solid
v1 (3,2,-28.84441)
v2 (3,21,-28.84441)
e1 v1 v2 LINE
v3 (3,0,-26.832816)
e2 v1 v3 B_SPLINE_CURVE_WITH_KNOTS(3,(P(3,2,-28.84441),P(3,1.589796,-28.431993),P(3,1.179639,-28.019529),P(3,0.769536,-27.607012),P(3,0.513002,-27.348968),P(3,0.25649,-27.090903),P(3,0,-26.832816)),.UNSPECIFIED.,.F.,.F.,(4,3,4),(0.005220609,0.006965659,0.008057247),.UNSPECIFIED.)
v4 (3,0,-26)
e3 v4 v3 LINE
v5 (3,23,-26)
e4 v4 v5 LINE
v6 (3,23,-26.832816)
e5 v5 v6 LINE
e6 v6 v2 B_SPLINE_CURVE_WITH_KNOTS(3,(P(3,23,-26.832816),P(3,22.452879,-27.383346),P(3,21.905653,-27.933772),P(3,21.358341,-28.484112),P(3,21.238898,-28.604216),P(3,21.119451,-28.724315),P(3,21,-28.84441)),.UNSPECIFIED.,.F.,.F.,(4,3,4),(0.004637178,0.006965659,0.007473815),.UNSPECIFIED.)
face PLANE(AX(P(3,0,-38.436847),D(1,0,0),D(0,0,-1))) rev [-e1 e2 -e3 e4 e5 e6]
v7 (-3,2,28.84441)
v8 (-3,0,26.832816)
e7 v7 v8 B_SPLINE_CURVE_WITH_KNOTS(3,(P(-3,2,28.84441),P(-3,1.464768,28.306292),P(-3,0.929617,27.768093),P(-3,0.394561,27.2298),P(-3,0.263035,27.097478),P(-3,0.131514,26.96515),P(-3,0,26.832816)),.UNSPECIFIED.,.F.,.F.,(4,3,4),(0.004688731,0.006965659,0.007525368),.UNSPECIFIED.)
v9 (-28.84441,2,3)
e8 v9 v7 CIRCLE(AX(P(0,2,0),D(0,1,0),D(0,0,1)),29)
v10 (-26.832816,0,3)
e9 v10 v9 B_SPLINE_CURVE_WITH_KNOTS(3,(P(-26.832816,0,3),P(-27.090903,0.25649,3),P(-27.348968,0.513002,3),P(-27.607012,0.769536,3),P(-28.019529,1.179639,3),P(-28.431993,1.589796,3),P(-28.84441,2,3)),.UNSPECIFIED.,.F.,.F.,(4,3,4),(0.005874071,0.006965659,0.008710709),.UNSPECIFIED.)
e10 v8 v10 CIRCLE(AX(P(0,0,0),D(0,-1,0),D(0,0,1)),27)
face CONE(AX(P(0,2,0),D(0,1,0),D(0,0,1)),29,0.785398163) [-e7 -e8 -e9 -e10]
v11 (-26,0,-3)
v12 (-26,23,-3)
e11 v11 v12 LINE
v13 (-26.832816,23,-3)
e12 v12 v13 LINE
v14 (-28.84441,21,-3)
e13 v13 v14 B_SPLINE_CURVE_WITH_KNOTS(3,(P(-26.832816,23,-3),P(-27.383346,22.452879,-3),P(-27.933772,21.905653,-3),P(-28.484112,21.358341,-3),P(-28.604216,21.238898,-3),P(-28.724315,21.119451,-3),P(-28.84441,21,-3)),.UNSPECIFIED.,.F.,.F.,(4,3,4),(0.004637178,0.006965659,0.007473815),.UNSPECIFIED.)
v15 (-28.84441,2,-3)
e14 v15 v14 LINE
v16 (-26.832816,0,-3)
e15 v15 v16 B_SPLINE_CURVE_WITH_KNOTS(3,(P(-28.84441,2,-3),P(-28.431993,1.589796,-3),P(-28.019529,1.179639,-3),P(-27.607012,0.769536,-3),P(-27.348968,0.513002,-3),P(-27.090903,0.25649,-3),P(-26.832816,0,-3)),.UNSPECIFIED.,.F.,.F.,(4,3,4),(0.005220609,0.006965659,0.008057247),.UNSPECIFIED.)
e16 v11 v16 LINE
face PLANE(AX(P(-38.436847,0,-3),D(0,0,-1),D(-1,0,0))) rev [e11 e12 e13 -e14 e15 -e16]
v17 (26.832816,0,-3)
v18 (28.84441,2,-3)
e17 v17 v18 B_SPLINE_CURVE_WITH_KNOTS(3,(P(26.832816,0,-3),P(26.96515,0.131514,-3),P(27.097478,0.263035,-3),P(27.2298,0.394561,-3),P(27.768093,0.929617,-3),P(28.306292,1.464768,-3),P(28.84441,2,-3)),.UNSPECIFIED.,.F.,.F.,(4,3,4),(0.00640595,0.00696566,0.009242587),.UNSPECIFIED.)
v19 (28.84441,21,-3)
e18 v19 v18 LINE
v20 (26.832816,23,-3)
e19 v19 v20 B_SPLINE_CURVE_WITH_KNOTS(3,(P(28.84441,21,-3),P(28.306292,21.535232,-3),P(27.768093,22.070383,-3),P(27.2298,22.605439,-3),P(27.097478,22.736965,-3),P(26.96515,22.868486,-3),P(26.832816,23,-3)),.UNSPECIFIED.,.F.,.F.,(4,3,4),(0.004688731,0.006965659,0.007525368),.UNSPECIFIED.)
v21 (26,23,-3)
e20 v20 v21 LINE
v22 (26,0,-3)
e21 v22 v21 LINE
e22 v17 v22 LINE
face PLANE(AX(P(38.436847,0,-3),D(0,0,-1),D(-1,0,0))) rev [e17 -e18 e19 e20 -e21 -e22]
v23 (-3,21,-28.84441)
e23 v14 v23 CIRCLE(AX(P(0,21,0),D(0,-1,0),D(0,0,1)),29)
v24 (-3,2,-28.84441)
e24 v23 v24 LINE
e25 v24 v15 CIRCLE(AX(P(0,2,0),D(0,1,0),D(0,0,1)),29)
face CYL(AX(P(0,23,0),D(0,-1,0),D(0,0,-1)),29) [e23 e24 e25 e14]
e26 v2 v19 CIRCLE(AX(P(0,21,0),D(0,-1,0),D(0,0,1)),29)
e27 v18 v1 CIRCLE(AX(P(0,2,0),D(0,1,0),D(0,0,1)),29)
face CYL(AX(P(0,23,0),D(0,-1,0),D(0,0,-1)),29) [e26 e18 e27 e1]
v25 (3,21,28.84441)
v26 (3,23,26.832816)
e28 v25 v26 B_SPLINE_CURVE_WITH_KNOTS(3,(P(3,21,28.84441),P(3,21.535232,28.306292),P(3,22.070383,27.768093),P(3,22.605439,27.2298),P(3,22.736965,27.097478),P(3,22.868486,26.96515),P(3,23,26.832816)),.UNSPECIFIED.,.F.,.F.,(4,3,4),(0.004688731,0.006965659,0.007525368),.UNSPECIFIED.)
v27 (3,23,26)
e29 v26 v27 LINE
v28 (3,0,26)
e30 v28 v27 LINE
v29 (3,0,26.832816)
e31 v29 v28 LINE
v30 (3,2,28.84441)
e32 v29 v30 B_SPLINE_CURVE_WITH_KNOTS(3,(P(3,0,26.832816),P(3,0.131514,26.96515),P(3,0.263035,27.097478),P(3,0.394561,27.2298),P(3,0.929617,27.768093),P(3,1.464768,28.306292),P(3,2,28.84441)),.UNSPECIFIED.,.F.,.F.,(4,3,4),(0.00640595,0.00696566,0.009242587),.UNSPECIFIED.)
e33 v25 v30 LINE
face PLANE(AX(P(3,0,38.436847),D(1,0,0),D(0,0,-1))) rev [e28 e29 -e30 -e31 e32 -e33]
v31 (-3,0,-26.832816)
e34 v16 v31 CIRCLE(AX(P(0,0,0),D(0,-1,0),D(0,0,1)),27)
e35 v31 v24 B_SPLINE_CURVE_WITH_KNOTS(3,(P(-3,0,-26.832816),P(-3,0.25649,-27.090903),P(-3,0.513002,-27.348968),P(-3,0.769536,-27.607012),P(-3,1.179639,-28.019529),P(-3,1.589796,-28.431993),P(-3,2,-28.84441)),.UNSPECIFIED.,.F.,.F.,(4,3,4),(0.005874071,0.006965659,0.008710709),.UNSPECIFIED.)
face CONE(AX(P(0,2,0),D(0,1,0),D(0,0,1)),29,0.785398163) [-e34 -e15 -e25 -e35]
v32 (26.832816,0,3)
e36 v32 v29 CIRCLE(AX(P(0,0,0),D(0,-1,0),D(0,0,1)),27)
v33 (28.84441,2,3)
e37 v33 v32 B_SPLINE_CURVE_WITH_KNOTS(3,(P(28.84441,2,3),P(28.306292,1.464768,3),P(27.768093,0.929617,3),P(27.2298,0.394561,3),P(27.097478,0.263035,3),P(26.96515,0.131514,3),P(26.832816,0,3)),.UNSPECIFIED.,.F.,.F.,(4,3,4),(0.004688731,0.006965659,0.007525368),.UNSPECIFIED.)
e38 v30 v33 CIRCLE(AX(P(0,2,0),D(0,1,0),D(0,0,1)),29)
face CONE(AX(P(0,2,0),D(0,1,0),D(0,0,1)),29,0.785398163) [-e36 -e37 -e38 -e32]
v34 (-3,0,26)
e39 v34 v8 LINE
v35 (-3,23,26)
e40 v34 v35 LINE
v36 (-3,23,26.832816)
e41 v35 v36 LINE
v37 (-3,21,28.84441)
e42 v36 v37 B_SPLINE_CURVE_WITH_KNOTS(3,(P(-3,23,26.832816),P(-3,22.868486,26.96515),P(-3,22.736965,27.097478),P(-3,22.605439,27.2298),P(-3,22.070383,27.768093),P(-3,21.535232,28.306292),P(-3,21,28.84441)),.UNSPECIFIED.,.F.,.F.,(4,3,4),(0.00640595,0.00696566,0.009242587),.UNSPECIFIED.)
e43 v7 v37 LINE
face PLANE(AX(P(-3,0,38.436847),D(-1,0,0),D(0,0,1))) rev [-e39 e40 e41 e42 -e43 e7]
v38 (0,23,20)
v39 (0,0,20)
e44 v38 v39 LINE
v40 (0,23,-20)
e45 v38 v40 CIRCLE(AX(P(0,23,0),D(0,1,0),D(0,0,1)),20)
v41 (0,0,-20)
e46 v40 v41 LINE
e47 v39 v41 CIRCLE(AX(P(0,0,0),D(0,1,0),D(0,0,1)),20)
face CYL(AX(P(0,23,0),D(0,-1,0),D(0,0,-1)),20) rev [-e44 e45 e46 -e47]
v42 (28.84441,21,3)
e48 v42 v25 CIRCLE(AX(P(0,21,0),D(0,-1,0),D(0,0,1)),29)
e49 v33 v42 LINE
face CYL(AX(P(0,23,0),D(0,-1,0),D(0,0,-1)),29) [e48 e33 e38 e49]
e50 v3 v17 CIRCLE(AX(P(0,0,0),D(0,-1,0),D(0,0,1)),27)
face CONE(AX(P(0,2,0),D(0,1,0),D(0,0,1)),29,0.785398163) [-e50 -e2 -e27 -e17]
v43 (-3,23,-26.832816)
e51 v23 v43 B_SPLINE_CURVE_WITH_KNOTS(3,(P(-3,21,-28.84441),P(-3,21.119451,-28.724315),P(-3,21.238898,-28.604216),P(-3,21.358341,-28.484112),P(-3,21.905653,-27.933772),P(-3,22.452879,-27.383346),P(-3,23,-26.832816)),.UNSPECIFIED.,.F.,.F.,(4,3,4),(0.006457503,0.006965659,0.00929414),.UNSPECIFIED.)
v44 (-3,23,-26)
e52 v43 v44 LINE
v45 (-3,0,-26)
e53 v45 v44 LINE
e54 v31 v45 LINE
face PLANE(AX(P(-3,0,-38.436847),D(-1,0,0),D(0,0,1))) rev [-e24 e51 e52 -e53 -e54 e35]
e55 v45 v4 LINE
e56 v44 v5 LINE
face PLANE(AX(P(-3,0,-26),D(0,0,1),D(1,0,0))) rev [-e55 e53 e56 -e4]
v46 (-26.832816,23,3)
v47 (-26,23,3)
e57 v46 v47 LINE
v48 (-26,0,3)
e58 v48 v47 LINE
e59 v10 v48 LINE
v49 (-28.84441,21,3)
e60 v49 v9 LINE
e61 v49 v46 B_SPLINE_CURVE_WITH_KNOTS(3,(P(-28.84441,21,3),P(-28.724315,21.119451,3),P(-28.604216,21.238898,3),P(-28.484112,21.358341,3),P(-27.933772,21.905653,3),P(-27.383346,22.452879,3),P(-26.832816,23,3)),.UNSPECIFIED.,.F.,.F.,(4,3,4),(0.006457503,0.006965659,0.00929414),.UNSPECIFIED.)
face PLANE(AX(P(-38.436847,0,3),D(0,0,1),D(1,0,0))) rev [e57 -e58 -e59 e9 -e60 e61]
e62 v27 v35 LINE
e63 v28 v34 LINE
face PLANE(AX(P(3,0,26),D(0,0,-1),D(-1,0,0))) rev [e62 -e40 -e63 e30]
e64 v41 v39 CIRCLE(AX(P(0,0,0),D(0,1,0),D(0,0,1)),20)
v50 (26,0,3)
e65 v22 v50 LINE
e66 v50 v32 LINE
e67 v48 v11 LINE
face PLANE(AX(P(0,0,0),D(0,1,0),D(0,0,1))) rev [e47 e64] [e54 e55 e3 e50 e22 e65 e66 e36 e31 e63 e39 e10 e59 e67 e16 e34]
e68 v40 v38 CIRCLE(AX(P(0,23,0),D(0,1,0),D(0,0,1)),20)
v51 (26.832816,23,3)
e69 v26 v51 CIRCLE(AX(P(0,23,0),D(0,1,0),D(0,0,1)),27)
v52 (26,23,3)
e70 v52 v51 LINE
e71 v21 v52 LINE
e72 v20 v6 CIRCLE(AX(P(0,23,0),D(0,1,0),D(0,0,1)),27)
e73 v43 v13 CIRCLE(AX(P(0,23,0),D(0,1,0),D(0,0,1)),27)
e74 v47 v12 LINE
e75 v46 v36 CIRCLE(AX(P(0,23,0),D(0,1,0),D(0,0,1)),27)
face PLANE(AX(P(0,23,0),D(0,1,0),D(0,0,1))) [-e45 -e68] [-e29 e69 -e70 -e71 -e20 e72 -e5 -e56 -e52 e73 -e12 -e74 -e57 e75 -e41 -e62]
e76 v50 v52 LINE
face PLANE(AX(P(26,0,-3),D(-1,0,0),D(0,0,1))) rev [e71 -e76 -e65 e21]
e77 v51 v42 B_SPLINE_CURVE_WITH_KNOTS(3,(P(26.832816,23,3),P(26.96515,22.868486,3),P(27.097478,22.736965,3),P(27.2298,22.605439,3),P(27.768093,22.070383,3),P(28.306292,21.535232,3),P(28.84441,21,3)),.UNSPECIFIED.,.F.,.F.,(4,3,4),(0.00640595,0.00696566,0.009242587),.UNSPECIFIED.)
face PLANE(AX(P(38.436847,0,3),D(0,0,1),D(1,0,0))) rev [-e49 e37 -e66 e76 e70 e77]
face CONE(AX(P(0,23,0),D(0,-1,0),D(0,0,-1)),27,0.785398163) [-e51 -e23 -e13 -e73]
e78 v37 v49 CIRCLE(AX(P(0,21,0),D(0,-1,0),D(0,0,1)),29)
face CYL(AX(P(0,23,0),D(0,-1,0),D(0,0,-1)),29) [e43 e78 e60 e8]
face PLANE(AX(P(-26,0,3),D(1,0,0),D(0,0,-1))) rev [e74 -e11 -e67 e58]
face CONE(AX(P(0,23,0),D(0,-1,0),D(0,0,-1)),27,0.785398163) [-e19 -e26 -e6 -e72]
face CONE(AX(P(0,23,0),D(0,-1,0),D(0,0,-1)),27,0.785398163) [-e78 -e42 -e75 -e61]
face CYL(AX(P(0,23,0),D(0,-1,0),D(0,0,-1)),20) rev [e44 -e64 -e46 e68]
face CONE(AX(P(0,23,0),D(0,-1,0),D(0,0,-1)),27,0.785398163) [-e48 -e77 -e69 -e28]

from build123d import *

# Parameters (mm, degrees)
SKETCH1_R           = 29
SKETCH1_R_2         = 20
BOSS_EXTRUDE1_DEPTH = 23
CHAMFER1_SIZE       = 2
SKETCH2_W           = 6
SKETCH2_H           = 12.436847424
CUT_EXTRUDE1_DEPTH  = 48.021271782
CIRPATTERN1_COUNT   = 4


with BuildPart() as part:
    # Sketch1 → Boss-Extrude1 (new body)
    with BuildSketch(Plane(origin=(0, 0, 0), x_dir=(1, 0, 0), z_dir=(0, 1, 0))):
        with Locations(Location((0, 0, 0), (0, 0, 270))):
            Circle(SKETCH1_R)
        with Locations(Location((0, 0, 0), (0, 0, 270))):
            Circle(SKETCH1_R_2, mode=Mode.SUBTRACT)
    extrude(amount=BOSS_EXTRUDE1_DEPTH)

    # Chamfer1
    chamfer1_edges = [part.edges().sort_by_distance(p)[0] for p in [
        (0, 0, -29),
        (0, 23, -29),
    ]]
    chamfer(chamfer1_edges, length=CHAMFER1_SIZE)

    # Sketch2 → Cut-Extrude1 (cut, through all)
    with BuildSketch(Plane(origin=(0, 23, 0), x_dir=(1, 0, 0), z_dir=(0, 1, 0))):
        with Locations((0, 32.218423712)):
            Rectangle(SKETCH2_W, SKETCH2_H)
    cut_extrude1 = extrude(amount=-CUT_EXTRUDE1_DEPTH, mode=Mode.SUBTRACT)

    # CirPattern1: Cut-Extrude1 ×4 about axis
    cirpattern1_axis = Axis((0, 0, 0), (0, 1, 0))
    for i in range(1, CIRPATTERN1_COUNT):
        add(cut_extrude1.rotate(cirpattern1_axis, i * 360 / CIRPATTERN1_COUNT), mode=Mode.SUBTRACT)


solid = part.part
